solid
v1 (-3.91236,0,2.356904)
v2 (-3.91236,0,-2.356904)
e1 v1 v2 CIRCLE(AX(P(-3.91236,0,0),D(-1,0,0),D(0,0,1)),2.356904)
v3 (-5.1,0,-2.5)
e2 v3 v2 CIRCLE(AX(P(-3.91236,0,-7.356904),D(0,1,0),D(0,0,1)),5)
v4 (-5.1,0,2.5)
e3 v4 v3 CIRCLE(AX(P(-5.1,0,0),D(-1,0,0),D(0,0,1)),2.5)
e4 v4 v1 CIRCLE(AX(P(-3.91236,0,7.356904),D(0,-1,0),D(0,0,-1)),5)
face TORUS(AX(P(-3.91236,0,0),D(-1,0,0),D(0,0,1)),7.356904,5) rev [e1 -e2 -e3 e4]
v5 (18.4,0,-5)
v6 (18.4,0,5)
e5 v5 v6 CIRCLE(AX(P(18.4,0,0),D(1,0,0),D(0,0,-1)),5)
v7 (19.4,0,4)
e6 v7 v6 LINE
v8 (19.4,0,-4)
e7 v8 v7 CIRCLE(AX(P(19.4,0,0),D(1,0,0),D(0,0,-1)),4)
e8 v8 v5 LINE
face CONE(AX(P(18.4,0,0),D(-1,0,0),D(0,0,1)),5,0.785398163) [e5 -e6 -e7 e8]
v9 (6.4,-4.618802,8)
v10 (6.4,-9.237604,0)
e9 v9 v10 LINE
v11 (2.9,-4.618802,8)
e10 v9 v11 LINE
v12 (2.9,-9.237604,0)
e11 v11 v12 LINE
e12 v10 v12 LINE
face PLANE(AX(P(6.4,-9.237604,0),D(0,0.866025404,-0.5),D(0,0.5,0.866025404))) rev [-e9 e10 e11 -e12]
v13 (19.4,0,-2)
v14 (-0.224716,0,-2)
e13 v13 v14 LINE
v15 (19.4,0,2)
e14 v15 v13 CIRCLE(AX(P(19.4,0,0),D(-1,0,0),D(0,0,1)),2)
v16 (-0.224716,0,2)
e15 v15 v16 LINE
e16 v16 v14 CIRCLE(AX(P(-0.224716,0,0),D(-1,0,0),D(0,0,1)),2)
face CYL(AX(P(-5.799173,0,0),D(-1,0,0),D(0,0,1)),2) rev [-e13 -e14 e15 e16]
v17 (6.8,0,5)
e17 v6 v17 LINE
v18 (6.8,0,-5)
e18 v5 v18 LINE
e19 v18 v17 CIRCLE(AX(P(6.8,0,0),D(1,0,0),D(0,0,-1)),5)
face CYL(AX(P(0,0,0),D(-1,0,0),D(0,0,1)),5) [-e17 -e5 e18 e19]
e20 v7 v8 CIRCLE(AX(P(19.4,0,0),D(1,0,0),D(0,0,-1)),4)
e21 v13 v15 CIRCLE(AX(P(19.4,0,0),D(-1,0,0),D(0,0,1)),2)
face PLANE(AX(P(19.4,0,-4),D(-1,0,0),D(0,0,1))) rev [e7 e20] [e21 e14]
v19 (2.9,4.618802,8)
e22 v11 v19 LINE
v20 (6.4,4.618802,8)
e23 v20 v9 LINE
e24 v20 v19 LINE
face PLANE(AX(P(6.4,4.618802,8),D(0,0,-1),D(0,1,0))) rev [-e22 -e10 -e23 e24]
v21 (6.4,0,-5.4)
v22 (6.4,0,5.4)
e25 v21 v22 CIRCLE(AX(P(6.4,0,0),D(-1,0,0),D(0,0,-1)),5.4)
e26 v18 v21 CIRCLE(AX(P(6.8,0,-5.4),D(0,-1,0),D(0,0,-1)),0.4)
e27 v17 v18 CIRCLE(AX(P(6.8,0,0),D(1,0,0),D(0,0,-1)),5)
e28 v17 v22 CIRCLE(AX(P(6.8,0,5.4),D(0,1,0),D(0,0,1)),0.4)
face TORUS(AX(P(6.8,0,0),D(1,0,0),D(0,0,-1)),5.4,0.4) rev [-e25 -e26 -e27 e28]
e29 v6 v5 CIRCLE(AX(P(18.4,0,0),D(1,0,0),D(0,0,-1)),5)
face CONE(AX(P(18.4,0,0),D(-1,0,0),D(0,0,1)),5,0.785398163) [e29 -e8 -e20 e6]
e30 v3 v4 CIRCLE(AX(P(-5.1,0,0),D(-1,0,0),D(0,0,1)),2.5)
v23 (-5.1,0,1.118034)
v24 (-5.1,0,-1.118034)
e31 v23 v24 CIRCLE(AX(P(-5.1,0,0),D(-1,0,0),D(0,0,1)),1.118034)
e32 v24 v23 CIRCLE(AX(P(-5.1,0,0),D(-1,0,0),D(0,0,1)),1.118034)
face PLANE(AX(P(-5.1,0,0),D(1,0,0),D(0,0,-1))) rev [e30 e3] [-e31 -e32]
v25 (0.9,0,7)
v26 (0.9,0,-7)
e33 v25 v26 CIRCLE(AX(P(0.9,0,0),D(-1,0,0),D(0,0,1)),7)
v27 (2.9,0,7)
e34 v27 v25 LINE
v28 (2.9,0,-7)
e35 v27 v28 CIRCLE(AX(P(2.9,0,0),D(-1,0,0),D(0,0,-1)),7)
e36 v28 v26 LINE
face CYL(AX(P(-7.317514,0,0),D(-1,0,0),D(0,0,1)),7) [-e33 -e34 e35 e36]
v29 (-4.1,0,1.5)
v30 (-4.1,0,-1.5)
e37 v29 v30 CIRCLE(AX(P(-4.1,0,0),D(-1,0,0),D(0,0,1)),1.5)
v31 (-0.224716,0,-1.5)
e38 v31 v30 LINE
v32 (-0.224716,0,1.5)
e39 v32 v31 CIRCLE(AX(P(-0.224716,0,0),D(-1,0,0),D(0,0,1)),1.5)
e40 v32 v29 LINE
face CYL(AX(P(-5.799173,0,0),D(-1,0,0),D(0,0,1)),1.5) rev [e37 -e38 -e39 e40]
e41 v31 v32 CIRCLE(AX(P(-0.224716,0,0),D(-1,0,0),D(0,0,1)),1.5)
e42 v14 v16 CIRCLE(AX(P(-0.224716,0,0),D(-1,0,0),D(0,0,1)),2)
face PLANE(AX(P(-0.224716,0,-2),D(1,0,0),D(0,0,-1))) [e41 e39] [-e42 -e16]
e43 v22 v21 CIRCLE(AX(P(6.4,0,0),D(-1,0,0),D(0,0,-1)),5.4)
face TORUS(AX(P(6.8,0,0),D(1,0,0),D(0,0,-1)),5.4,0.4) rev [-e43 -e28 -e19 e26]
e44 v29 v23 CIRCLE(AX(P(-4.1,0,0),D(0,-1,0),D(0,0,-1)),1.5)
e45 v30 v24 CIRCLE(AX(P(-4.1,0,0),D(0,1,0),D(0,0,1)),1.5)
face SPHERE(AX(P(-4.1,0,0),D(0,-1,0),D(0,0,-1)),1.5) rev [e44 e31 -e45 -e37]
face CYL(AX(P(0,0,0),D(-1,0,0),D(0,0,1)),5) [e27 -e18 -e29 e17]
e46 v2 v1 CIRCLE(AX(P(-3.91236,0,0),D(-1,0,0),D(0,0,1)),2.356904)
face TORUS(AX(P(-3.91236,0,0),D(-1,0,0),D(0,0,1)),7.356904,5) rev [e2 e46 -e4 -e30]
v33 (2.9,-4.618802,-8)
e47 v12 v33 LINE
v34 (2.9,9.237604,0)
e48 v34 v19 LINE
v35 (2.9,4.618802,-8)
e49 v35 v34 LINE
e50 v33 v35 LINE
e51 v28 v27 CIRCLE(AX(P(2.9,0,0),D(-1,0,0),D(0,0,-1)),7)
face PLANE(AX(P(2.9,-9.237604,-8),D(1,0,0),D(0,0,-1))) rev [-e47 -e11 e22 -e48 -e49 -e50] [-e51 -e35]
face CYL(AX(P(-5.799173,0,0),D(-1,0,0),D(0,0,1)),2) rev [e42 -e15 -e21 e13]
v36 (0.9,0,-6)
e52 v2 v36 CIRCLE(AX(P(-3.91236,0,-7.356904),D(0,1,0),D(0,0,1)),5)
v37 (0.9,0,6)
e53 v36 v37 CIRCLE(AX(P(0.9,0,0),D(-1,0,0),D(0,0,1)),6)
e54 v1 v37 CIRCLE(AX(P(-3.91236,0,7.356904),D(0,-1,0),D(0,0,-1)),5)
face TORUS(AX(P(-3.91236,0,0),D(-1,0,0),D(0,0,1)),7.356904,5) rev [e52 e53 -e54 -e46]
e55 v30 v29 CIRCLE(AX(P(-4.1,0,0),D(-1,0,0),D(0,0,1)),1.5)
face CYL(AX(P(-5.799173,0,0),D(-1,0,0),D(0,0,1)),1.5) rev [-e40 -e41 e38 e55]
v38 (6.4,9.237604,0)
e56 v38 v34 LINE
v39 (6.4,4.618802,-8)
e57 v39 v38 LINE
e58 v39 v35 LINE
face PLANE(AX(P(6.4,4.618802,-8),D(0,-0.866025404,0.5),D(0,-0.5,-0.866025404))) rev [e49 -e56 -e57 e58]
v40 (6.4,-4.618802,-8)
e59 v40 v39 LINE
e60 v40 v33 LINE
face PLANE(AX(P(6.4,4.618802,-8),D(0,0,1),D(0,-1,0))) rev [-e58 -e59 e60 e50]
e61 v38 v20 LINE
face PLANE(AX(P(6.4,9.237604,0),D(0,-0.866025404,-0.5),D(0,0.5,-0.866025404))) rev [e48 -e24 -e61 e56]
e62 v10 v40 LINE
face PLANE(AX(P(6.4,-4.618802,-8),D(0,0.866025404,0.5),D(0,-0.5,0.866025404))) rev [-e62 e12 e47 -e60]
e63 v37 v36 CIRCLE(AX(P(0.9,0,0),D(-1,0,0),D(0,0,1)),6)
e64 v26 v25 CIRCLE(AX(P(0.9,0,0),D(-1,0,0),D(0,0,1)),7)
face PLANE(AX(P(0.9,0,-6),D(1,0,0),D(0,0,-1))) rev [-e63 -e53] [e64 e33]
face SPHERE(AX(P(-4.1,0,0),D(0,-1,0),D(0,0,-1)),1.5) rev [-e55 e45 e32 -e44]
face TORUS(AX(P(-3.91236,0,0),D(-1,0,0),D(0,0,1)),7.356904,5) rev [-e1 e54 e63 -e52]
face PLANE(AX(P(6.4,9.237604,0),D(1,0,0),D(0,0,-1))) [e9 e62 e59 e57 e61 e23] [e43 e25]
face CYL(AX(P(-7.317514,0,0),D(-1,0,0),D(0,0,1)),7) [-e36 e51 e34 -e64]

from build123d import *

# Parameters (mm, degrees)
BASE_EXTRUDE_DEPTH      = 6.4
FILLET_2_R              = 0.4
CUT_EXTRUDE1_DEPTH      = 23.928003257
CUT_EXTRUDE1_DEPTH_BACK = 23.928003257
SKETCH8_W               = 2.9
SKETCH8_H               = 16


with BuildPart() as part:
    # Sketch1 → Base-Extrude (new body)
    with BuildSketch(Plane(origin=(0, 0, 0), x_dir=(0, 0, -1), z_dir=(1, 0, 0))):
        Polygon((8, 4.618802154), (8, -4.618802154), (0, -9.237604307), (-8, -4.618802154), (-8, 4.618802154), (0, 9.237604307), align=None)
    extrude(amount=BASE_EXTRUDE_DEPTH)

    # Sketch2 → Boss-Revolve1 (revolve)
    with BuildSketch(Plane.XY, mode=Mode.PRIVATE) as boss_revolve1_sk:
        Polygon((0, 0), (32.4, 0), (32.4, 4.134), (32.4, 5), (27.8072, 5), (0, 5), align=None)
    revolve(boss_revolve1_sk.sketch.rotate(Axis((0, 0, 0), (1, 0, 0)), 90), axis=Axis((0, 0, 0), (1, 0, 0)))

    # Sketch3 → Cut-Revolve1 (revolve, cut)
    with BuildSketch(Plane.XY):
        Polygon((0, 8), (3.601282526, 14.237604307), (3.601282526, 19.237604307), (-10, 19.237604307), (-10, 8), align=None)
    revolve(axis=Axis((0, 0, 0), (1, 0, 0)), mode=Mode.SUBTRACT)

    # Fillet 2
    fillet_2_edges = [part.edges().sort_by_distance(p)[0] for p in [
        (6.4, 0, -5),
    ]]
    fillet(fillet_2_edges, radius=FILLET_2_R)

    # Sketch7 → Cut-Revolve5 (revolve, cut)
    with BuildSketch(Plane(origin=(0, 0, 0), x_dir=(1, 0, 0), z_dir=(0, 1, 0))):
        Polygon((32.4, 5), (18.4, 5), (19.4, 4), (19.4, 0), (32.4, 0), align=None)
    revolve(axis=Axis((34.209458749, 0, 0), (-1, 0, 0)), mode=Mode.SUBTRACT)

    # Sketch8 → Cut-Extrude1 (cut, two sides: drawn at the far end of the back side and taken through both)
    with BuildSketch(Plane(origin=(0, 0, 0), x_dir=(1, 0, 0), z_dir=(0, 1, 0)).offset(-CUT_EXTRUDE1_DEPTH_BACK)):
        with Locations((1.45, 0)):
            Rectangle(SKETCH8_W, SKETCH8_H)
    extrude(amount=CUT_EXTRUDE1_DEPTH + CUT_EXTRUDE1_DEPTH_BACK, mode=Mode.SUBTRACT)

    # Sketch9 → Revolve1 (revolve)
    with BuildSketch(Plane(origin=(0, 0, 0), x_dir=(1, 0, 0), z_dir=(0, 1, 0))):
        with BuildLine():
            Line((-5.1, 0), (-5.1, 2.5))
            ThreePointArc((-5.1, 2.5), (-1.393005283, 3.038009057), (0.9, 6))
            Line((0.9, 6), (0.9, 7))
            Line((0.9, 7), (2.9, 7))
            Line((2.9, 7), (2.9, 0))
            Line((2.9, 0), (-5.1, 0))
        make_face()
    revolve(axis=Axis((-7.317514451, 0, 0), (1, 0, 0)))

    # Sketch10 → Cut-Revolve6 (revolve, cut)
    with BuildSketch(Plane(origin=(0, 0, 0), x_dir=(1, 0, 0), z_dir=(0, 1, 0)), mode=Mode.PRIVATE) as cut_revolve6_sk:
        with BuildLine():
            Line((19.4, 0), (19.4, 2))
            Line((19.4, 2), (-0.22471637, 2))
            Line((-0.22471637, 2), (-0.22471637, 1.5))
            Line((-0.22471637, 1.5), (-4.1, 1.5))
            ThreePointArc((-4.1, 1.5), (-4.635233135, 1.401258538), (-5.1, 1.118033989))
            Line((-5.1, 1.118033989), (-5.1, 0))
            Line((-5.1, 0), (19.4, 0))
        make_face()
    revolve(cut_revolve6_sk.sketch.rotate(Axis((-5.799172577, 0, 0), (1, 0, 0)), 180), axis=Axis((-5.799172577, 0, 0), (1, 0, 0)), mode=Mode.SUBTRACT)


solid = part.part
